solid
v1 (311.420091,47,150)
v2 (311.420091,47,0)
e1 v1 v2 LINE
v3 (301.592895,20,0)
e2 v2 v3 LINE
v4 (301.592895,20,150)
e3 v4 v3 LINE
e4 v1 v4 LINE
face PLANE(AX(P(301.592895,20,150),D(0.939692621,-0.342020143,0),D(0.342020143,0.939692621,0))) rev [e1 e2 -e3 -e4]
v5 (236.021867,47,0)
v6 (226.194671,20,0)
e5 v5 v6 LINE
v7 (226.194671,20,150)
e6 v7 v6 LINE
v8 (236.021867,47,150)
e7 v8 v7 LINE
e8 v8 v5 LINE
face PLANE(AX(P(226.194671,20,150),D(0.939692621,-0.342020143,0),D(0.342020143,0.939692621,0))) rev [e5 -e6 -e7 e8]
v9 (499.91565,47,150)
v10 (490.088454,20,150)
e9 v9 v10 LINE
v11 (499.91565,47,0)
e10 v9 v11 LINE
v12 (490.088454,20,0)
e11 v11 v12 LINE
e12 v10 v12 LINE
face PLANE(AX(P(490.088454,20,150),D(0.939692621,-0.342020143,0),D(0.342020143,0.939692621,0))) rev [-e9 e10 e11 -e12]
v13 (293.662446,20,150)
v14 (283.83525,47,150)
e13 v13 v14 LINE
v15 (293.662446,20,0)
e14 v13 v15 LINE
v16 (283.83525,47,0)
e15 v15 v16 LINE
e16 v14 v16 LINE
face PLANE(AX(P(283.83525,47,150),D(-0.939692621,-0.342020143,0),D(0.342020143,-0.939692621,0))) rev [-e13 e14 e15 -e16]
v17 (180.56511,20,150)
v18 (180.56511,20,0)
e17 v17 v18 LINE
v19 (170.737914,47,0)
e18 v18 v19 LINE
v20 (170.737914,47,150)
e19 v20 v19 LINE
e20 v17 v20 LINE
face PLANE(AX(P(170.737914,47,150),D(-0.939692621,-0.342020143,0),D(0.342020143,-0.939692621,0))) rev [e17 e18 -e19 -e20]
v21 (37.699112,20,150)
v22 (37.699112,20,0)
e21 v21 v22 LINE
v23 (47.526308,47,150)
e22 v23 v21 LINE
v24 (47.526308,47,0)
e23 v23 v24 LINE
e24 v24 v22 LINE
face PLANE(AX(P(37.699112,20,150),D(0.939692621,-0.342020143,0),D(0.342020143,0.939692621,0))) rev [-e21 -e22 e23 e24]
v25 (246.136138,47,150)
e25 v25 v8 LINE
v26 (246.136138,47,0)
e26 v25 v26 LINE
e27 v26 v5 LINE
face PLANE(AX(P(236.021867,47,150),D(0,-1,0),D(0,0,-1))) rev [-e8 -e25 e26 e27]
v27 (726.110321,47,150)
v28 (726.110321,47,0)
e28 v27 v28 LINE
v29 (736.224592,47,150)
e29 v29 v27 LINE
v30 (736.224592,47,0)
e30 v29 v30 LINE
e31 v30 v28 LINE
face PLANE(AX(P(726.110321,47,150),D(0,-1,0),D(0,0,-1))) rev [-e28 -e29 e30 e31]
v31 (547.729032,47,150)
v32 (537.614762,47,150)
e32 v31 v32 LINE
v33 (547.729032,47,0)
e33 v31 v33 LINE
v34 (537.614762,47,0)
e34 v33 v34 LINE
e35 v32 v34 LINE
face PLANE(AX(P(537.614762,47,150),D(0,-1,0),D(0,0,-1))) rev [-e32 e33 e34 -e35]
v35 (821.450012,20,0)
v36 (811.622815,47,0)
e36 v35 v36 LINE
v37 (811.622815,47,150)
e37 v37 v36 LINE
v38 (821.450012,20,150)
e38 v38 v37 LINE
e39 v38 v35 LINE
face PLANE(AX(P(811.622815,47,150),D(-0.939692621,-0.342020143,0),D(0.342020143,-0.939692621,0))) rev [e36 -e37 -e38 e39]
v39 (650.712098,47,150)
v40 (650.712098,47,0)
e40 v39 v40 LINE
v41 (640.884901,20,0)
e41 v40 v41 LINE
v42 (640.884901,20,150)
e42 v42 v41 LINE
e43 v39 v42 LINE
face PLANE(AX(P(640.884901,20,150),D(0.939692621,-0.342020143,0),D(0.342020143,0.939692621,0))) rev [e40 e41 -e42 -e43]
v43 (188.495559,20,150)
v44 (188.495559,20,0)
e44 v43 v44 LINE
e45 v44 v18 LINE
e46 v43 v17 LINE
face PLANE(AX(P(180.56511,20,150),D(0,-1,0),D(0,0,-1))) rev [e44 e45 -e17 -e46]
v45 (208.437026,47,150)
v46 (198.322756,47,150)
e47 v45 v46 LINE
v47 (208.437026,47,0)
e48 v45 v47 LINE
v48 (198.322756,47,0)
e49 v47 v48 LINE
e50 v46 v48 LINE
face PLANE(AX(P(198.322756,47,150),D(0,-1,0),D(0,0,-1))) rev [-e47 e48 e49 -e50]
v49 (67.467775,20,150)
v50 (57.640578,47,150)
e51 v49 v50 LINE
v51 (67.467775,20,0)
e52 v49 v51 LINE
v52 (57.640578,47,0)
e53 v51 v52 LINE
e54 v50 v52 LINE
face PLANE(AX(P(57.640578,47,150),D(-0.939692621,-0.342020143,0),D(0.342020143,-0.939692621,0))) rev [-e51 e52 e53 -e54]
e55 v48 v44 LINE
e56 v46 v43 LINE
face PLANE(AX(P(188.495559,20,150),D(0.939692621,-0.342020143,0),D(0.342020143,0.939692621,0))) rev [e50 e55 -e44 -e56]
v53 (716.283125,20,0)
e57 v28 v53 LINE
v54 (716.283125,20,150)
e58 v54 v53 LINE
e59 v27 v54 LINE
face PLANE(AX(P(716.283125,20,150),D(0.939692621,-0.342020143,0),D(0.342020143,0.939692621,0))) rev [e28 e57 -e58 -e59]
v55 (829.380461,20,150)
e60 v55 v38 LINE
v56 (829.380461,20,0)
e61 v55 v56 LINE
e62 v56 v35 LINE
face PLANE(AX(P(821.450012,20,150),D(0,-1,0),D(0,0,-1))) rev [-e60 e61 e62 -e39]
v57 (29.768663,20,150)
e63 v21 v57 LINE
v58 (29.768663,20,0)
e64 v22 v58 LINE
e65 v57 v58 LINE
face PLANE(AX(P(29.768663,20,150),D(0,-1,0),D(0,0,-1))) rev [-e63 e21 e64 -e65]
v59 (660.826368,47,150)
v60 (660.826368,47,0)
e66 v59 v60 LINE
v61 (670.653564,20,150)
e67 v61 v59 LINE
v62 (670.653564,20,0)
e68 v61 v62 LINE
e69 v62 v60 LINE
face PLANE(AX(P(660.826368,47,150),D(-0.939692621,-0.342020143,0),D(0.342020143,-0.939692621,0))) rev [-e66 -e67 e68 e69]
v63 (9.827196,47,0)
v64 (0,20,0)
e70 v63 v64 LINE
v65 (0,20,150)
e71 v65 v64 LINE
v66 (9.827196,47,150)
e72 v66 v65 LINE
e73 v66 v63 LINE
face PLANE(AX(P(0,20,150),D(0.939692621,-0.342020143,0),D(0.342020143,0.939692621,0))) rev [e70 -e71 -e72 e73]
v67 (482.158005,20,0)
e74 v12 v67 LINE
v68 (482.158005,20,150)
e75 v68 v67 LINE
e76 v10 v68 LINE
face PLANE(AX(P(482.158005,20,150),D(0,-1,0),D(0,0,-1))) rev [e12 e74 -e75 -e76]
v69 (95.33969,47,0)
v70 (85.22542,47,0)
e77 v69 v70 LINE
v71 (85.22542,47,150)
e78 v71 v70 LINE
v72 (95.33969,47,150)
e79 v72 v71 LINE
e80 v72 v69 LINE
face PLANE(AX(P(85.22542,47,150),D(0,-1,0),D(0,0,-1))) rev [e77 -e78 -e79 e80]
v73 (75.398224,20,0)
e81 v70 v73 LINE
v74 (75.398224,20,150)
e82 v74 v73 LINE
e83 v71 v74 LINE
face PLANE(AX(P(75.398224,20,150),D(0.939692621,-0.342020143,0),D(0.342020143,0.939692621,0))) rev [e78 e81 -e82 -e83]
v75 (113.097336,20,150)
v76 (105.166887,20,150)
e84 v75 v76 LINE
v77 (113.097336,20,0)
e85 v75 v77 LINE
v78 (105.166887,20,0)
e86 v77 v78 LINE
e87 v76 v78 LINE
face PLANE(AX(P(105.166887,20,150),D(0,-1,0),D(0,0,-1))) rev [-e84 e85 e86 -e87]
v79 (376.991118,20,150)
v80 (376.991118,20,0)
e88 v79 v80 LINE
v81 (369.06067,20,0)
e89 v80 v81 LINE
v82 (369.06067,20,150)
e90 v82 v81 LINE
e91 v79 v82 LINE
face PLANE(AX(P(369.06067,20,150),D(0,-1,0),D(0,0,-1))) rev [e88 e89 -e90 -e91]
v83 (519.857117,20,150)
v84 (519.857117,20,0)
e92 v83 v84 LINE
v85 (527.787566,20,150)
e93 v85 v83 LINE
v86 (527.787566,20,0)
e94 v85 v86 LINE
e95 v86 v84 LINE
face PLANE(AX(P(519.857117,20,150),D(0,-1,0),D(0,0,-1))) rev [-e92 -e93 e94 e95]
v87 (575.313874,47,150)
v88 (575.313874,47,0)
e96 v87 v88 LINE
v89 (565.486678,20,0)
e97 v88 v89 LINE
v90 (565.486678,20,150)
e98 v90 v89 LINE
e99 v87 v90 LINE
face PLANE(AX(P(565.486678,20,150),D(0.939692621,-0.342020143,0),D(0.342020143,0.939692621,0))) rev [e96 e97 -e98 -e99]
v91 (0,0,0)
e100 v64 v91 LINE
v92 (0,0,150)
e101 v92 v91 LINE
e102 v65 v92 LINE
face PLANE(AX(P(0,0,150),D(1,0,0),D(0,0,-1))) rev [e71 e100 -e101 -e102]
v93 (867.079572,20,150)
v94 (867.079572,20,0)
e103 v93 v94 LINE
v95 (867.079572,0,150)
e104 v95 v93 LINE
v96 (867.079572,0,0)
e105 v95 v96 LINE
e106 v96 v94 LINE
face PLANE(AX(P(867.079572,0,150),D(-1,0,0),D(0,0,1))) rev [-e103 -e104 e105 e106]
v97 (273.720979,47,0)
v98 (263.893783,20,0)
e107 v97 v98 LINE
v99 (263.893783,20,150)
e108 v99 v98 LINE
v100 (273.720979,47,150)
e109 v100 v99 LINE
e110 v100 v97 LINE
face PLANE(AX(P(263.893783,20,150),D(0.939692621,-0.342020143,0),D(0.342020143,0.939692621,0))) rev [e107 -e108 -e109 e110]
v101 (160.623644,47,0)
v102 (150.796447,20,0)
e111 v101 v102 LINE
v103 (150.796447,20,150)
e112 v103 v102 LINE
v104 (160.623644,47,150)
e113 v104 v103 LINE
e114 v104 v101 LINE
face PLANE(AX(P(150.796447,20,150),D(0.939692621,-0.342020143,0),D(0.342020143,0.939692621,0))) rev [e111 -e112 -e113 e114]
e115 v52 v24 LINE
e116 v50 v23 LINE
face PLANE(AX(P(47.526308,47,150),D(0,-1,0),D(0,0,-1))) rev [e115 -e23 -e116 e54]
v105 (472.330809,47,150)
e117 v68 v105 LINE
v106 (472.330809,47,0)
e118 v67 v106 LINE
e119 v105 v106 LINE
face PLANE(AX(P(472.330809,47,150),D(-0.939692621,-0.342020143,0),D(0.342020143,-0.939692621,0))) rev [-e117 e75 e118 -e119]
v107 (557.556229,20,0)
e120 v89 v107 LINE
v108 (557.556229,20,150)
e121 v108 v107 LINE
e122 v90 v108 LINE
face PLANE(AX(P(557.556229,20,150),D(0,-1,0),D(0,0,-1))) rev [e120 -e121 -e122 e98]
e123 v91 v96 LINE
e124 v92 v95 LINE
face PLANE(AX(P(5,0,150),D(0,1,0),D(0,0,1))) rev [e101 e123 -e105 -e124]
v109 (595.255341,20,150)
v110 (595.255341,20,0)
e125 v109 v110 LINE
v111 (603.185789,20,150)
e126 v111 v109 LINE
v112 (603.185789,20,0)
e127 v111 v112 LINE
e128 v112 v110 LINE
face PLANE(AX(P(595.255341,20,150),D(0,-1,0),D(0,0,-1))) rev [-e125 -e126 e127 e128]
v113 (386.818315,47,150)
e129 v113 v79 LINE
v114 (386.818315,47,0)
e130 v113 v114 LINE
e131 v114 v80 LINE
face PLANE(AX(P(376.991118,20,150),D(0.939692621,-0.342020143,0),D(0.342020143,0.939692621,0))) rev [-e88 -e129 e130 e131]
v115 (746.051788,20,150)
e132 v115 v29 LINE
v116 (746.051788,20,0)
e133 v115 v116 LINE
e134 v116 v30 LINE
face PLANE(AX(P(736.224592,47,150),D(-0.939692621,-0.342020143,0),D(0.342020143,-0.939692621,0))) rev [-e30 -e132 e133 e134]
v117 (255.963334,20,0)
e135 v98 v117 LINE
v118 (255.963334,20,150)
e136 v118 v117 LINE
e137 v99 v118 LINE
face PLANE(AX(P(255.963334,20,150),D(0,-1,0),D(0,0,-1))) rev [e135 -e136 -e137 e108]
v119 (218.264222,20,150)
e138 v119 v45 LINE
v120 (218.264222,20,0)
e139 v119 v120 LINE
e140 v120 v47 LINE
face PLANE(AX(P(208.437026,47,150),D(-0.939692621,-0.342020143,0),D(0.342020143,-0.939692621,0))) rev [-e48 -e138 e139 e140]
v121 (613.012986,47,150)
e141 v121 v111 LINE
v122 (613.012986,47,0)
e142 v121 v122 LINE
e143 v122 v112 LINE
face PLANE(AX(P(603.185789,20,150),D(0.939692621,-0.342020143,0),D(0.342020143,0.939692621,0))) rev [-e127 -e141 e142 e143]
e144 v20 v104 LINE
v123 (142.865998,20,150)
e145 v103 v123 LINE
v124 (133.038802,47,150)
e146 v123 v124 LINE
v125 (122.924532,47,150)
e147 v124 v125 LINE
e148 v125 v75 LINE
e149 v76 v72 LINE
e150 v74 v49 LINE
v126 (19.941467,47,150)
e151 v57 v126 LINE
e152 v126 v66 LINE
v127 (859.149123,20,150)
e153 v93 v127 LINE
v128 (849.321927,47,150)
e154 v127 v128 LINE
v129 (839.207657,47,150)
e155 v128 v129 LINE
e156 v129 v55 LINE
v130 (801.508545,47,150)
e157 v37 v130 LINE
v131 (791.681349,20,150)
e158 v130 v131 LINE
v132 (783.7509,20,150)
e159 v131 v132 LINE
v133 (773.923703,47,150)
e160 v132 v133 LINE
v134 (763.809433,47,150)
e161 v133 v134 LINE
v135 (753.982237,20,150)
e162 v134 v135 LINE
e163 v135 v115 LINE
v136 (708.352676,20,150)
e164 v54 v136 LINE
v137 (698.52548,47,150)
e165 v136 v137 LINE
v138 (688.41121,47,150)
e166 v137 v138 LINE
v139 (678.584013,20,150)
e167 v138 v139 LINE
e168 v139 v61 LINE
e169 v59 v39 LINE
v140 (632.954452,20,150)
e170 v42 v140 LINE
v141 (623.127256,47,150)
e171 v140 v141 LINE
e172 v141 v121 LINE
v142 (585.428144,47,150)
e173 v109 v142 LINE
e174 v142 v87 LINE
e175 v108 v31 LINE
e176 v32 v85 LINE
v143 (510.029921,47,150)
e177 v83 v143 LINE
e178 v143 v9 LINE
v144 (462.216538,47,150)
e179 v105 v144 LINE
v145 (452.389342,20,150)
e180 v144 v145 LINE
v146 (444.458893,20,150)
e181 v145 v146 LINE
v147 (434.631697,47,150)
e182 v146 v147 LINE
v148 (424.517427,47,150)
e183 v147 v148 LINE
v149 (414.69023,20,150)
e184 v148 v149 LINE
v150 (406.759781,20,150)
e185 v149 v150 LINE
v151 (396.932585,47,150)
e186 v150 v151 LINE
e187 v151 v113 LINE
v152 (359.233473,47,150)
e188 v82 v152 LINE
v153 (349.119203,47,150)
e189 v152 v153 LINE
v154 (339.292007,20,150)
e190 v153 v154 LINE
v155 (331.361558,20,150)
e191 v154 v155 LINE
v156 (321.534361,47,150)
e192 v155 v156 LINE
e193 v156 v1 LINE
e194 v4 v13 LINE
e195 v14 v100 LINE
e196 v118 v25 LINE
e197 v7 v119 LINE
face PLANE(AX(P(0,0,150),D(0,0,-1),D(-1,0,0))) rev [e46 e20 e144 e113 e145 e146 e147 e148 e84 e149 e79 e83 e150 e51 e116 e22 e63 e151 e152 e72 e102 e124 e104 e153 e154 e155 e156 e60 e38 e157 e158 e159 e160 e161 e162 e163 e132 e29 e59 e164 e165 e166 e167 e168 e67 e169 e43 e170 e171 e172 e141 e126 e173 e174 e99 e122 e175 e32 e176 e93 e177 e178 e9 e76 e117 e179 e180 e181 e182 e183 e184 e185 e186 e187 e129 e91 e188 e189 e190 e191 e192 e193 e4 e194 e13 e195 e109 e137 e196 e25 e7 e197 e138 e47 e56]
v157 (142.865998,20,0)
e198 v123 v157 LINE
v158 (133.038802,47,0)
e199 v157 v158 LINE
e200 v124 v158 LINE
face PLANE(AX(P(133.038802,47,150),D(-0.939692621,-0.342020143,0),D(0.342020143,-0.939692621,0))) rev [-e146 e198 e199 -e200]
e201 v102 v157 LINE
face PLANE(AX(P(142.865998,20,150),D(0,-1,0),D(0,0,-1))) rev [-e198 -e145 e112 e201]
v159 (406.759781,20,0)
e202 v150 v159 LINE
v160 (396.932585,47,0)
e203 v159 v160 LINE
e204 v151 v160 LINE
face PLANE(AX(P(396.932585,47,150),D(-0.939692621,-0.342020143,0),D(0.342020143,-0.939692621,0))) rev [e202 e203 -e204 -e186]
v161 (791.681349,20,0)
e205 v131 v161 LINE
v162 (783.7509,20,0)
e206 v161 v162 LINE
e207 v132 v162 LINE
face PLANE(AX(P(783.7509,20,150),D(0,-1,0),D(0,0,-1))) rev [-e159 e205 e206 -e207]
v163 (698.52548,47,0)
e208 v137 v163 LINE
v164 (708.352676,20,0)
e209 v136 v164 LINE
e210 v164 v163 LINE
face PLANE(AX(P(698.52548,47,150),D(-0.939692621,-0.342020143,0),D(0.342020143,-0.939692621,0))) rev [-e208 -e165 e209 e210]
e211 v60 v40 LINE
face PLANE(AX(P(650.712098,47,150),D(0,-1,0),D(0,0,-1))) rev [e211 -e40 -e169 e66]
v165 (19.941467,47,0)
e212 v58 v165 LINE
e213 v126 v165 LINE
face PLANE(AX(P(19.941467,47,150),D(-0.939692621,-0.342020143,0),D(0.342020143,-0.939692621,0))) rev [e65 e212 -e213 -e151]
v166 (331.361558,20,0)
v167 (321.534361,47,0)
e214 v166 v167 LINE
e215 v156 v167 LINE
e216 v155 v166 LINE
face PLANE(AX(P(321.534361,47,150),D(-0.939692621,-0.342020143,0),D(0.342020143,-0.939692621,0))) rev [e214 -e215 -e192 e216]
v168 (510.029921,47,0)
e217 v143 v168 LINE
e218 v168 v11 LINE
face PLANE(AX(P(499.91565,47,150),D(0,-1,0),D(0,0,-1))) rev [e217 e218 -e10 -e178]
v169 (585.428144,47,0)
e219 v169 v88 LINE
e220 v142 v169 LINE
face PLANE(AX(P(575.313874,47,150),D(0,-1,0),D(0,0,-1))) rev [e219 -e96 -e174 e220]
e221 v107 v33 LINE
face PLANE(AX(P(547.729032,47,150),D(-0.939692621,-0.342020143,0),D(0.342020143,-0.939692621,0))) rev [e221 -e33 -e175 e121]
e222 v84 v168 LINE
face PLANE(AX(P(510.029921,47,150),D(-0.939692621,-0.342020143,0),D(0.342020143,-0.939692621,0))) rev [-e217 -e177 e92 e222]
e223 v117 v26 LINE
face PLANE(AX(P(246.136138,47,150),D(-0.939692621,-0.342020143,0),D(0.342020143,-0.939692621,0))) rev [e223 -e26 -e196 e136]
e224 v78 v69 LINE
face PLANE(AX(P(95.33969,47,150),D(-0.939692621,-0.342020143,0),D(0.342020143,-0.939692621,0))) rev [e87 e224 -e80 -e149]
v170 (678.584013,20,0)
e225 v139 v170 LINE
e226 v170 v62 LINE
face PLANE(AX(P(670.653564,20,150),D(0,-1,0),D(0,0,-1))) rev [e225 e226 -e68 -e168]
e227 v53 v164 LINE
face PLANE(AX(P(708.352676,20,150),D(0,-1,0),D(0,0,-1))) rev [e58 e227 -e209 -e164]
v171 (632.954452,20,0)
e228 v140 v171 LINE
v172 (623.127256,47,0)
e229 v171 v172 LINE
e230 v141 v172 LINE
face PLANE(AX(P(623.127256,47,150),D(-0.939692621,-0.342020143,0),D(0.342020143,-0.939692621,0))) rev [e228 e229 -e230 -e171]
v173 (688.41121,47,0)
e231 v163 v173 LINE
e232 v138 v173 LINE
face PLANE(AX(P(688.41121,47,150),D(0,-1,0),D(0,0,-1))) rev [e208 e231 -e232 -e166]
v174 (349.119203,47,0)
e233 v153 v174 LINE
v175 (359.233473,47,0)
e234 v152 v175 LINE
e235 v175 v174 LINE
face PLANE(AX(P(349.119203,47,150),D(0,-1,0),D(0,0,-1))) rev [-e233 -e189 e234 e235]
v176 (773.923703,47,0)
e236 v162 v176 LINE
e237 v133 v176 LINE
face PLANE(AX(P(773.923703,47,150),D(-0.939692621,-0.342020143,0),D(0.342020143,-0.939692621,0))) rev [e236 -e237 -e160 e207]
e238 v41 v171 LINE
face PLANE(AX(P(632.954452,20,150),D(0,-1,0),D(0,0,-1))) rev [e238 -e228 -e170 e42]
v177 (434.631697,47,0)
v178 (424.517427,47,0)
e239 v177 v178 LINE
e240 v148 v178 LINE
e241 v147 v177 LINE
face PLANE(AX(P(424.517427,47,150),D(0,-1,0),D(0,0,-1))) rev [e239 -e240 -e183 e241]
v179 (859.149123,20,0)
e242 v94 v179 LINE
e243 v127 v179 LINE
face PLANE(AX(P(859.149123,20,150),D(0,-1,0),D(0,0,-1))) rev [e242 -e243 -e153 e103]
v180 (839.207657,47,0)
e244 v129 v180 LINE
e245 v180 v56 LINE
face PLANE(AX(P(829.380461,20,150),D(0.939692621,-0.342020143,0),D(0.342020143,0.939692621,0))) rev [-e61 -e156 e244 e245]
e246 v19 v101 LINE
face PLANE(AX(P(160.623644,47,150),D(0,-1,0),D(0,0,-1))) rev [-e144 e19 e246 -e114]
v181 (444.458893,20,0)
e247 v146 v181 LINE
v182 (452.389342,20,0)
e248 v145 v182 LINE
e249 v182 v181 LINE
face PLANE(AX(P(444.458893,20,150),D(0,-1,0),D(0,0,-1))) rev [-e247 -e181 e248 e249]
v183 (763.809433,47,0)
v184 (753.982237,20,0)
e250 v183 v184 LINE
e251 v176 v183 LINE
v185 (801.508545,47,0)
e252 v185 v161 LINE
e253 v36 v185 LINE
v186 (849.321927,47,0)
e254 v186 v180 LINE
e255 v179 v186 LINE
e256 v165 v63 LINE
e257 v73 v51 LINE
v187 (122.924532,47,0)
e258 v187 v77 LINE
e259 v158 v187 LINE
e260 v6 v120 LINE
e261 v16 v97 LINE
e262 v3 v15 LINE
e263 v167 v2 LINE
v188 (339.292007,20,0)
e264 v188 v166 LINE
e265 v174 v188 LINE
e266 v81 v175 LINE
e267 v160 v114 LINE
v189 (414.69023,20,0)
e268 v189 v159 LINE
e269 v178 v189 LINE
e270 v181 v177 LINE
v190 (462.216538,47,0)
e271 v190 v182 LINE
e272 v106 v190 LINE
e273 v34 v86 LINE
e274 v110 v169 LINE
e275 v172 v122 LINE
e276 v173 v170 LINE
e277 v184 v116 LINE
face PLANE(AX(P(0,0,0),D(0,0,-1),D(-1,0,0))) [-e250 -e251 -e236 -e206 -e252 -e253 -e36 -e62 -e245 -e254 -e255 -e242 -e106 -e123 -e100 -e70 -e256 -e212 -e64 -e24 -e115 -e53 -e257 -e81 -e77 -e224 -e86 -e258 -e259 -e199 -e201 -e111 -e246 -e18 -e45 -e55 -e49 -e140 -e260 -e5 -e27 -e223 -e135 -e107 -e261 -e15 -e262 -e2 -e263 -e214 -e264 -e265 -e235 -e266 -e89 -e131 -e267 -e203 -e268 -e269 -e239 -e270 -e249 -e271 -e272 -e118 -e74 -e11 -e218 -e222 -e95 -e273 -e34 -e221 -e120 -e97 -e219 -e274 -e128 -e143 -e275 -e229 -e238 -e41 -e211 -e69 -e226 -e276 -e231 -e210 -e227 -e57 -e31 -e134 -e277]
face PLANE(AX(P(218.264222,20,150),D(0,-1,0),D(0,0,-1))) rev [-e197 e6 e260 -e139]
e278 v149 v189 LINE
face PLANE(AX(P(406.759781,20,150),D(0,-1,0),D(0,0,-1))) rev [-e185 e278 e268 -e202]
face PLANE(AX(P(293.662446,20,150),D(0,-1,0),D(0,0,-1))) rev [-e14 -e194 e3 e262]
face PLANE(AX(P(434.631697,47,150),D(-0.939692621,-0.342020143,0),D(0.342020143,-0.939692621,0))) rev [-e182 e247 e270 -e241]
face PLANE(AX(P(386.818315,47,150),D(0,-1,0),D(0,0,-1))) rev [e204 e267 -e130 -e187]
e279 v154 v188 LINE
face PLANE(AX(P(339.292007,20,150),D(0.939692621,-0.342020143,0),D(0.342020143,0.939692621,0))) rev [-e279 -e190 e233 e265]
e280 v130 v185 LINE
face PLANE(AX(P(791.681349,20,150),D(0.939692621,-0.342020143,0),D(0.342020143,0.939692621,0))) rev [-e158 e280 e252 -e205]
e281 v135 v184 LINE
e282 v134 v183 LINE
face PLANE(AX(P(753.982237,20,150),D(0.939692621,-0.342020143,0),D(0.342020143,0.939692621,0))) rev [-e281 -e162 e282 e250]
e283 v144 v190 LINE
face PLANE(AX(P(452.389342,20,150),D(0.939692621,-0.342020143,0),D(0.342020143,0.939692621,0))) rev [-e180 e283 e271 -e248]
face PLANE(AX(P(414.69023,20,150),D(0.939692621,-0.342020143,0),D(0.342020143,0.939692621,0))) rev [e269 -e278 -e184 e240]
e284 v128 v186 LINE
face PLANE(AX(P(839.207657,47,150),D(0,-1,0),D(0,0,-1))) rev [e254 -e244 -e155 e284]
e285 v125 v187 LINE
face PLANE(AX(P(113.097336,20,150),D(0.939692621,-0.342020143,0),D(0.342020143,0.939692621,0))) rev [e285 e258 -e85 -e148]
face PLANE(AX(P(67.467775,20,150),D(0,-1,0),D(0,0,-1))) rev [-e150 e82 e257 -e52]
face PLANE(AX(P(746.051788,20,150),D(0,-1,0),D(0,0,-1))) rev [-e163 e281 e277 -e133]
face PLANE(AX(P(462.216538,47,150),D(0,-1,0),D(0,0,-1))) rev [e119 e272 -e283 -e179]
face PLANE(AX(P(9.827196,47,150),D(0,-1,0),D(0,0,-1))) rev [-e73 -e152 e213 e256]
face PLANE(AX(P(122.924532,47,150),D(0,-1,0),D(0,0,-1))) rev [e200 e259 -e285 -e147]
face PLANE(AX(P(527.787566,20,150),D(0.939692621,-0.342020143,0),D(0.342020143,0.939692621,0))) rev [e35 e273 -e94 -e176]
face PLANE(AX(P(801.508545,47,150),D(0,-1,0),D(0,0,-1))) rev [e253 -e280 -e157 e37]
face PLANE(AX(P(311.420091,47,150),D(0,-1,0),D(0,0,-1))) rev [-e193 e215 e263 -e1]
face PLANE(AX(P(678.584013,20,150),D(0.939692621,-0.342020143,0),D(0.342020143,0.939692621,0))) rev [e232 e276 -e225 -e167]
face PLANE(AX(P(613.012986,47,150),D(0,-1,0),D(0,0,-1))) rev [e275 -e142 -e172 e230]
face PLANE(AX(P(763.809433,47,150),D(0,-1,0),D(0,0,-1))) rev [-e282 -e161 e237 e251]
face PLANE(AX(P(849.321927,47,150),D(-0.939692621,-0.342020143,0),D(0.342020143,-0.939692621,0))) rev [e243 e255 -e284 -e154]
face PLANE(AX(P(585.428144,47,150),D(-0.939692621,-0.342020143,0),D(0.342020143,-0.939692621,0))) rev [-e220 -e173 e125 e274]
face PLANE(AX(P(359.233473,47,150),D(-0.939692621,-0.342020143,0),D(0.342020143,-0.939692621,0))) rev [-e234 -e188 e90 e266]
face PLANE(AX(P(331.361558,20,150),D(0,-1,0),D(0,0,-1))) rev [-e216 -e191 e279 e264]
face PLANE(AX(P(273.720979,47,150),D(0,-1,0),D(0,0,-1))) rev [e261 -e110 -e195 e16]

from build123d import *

# Parameters (mm, degrees)
SKETCH1_W           = 5
SKETCH1_H           = 5
BOSS_EXTRUDE1_DEPTH = 150
BOSS_EXTRUDE2_DEPTH = 150


with BuildPart() as part:
    # Sketch1 → Boss-Extrude1 (new body)
    with BuildSketch(Plane.XY):
        with Locations((2.5, 2.5)):
            Rectangle(SKETCH1_W, SKETCH1_H)
    extrude(amount=BOSS_EXTRUDE1_DEPTH)

    # Sketch2 → Boss-Extrude2 (add)
    with BuildSketch(Plane.XY):
        Polygon((0, 20), (9.827196325, 47), (19.941466624, 47), (29.76866295, 20), (37.699111843, 20), (47.526308168, 47), (57.640578467, 47), (67.467774793, 20), (75.398223686, 20), (85.225420011, 47), (95.33969031, 47), (105.166886636, 20), (113.097335529, 20), (122.924531854, 47), (133.038802154, 47), (142.865998479, 20), (150.796447372, 20), (160.623643697, 47), (170.737913997, 47), (180.565110322, 20), (188.495559215, 20), (198.322755541, 47), (208.43702584, 47), (218.264222165, 20), (226.194671058, 20), (236.021867384, 47), (246.136137683, 47), (255.963334008, 20), (263.893782902, 20), (273.720979227, 47), (283.835249526, 47), (293.662445851, 20), (301.592894745, 20), (311.42009107, 47), (321.534361369, 47), (331.361557694, 20), (339.292006588, 20), (349.119202913, 47), (359.233473212, 47), (369.060669537, 20), (376.991118431, 20), (386.818314756, 47), (396.932585055, 47), (406.75978138, 20), (414.690230274, 20), (424.517426599, 47), (434.631696898, 47), (444.458893223, 20), (452.389342117, 20), (462.216538442, 47), (472.330808741, 47), (482.158005066, 20), (490.08845396, 20), (499.915650285, 47), (510.029920584, 47), (519.85711691, 20), (527.787565803, 20), (537.614762128, 47), (547.729032427, 47), (557.556228753, 20), (565.486677646, 20), (575.313873971, 47), (585.42814427, 47), (595.255340596, 20), (603.185789489, 20), (613.012985814, 47), (623.127256114, 47), (632.954452439, 20), (640.884901332, 20), (650.712097658, 47), (660.826367957, 47), (670.653564282, 20), (678.584013175, 20), (688.411209501, 47), (698.5254798, 47), (708.352676125, 20), (716.283125018, 20), (726.110321344, 47), (736.224591643, 47), (746.051787968, 20), (753.982236862, 20), (763.809433187, 47), (773.923703486, 47), (783.750899811, 20), (791.681348705, 20), (801.50854503, 47), (811.622815329, 47), (821.450011654, 20), (829.380460548, 20), (839.207656873, 47), (849.321927172, 47), (859.149123497, 20), (867.079572391, 20), (867.079572391, 0), (0, 0), align=None)
    extrude(amount=BOSS_EXTRUDE2_DEPTH)


solid = part.part
